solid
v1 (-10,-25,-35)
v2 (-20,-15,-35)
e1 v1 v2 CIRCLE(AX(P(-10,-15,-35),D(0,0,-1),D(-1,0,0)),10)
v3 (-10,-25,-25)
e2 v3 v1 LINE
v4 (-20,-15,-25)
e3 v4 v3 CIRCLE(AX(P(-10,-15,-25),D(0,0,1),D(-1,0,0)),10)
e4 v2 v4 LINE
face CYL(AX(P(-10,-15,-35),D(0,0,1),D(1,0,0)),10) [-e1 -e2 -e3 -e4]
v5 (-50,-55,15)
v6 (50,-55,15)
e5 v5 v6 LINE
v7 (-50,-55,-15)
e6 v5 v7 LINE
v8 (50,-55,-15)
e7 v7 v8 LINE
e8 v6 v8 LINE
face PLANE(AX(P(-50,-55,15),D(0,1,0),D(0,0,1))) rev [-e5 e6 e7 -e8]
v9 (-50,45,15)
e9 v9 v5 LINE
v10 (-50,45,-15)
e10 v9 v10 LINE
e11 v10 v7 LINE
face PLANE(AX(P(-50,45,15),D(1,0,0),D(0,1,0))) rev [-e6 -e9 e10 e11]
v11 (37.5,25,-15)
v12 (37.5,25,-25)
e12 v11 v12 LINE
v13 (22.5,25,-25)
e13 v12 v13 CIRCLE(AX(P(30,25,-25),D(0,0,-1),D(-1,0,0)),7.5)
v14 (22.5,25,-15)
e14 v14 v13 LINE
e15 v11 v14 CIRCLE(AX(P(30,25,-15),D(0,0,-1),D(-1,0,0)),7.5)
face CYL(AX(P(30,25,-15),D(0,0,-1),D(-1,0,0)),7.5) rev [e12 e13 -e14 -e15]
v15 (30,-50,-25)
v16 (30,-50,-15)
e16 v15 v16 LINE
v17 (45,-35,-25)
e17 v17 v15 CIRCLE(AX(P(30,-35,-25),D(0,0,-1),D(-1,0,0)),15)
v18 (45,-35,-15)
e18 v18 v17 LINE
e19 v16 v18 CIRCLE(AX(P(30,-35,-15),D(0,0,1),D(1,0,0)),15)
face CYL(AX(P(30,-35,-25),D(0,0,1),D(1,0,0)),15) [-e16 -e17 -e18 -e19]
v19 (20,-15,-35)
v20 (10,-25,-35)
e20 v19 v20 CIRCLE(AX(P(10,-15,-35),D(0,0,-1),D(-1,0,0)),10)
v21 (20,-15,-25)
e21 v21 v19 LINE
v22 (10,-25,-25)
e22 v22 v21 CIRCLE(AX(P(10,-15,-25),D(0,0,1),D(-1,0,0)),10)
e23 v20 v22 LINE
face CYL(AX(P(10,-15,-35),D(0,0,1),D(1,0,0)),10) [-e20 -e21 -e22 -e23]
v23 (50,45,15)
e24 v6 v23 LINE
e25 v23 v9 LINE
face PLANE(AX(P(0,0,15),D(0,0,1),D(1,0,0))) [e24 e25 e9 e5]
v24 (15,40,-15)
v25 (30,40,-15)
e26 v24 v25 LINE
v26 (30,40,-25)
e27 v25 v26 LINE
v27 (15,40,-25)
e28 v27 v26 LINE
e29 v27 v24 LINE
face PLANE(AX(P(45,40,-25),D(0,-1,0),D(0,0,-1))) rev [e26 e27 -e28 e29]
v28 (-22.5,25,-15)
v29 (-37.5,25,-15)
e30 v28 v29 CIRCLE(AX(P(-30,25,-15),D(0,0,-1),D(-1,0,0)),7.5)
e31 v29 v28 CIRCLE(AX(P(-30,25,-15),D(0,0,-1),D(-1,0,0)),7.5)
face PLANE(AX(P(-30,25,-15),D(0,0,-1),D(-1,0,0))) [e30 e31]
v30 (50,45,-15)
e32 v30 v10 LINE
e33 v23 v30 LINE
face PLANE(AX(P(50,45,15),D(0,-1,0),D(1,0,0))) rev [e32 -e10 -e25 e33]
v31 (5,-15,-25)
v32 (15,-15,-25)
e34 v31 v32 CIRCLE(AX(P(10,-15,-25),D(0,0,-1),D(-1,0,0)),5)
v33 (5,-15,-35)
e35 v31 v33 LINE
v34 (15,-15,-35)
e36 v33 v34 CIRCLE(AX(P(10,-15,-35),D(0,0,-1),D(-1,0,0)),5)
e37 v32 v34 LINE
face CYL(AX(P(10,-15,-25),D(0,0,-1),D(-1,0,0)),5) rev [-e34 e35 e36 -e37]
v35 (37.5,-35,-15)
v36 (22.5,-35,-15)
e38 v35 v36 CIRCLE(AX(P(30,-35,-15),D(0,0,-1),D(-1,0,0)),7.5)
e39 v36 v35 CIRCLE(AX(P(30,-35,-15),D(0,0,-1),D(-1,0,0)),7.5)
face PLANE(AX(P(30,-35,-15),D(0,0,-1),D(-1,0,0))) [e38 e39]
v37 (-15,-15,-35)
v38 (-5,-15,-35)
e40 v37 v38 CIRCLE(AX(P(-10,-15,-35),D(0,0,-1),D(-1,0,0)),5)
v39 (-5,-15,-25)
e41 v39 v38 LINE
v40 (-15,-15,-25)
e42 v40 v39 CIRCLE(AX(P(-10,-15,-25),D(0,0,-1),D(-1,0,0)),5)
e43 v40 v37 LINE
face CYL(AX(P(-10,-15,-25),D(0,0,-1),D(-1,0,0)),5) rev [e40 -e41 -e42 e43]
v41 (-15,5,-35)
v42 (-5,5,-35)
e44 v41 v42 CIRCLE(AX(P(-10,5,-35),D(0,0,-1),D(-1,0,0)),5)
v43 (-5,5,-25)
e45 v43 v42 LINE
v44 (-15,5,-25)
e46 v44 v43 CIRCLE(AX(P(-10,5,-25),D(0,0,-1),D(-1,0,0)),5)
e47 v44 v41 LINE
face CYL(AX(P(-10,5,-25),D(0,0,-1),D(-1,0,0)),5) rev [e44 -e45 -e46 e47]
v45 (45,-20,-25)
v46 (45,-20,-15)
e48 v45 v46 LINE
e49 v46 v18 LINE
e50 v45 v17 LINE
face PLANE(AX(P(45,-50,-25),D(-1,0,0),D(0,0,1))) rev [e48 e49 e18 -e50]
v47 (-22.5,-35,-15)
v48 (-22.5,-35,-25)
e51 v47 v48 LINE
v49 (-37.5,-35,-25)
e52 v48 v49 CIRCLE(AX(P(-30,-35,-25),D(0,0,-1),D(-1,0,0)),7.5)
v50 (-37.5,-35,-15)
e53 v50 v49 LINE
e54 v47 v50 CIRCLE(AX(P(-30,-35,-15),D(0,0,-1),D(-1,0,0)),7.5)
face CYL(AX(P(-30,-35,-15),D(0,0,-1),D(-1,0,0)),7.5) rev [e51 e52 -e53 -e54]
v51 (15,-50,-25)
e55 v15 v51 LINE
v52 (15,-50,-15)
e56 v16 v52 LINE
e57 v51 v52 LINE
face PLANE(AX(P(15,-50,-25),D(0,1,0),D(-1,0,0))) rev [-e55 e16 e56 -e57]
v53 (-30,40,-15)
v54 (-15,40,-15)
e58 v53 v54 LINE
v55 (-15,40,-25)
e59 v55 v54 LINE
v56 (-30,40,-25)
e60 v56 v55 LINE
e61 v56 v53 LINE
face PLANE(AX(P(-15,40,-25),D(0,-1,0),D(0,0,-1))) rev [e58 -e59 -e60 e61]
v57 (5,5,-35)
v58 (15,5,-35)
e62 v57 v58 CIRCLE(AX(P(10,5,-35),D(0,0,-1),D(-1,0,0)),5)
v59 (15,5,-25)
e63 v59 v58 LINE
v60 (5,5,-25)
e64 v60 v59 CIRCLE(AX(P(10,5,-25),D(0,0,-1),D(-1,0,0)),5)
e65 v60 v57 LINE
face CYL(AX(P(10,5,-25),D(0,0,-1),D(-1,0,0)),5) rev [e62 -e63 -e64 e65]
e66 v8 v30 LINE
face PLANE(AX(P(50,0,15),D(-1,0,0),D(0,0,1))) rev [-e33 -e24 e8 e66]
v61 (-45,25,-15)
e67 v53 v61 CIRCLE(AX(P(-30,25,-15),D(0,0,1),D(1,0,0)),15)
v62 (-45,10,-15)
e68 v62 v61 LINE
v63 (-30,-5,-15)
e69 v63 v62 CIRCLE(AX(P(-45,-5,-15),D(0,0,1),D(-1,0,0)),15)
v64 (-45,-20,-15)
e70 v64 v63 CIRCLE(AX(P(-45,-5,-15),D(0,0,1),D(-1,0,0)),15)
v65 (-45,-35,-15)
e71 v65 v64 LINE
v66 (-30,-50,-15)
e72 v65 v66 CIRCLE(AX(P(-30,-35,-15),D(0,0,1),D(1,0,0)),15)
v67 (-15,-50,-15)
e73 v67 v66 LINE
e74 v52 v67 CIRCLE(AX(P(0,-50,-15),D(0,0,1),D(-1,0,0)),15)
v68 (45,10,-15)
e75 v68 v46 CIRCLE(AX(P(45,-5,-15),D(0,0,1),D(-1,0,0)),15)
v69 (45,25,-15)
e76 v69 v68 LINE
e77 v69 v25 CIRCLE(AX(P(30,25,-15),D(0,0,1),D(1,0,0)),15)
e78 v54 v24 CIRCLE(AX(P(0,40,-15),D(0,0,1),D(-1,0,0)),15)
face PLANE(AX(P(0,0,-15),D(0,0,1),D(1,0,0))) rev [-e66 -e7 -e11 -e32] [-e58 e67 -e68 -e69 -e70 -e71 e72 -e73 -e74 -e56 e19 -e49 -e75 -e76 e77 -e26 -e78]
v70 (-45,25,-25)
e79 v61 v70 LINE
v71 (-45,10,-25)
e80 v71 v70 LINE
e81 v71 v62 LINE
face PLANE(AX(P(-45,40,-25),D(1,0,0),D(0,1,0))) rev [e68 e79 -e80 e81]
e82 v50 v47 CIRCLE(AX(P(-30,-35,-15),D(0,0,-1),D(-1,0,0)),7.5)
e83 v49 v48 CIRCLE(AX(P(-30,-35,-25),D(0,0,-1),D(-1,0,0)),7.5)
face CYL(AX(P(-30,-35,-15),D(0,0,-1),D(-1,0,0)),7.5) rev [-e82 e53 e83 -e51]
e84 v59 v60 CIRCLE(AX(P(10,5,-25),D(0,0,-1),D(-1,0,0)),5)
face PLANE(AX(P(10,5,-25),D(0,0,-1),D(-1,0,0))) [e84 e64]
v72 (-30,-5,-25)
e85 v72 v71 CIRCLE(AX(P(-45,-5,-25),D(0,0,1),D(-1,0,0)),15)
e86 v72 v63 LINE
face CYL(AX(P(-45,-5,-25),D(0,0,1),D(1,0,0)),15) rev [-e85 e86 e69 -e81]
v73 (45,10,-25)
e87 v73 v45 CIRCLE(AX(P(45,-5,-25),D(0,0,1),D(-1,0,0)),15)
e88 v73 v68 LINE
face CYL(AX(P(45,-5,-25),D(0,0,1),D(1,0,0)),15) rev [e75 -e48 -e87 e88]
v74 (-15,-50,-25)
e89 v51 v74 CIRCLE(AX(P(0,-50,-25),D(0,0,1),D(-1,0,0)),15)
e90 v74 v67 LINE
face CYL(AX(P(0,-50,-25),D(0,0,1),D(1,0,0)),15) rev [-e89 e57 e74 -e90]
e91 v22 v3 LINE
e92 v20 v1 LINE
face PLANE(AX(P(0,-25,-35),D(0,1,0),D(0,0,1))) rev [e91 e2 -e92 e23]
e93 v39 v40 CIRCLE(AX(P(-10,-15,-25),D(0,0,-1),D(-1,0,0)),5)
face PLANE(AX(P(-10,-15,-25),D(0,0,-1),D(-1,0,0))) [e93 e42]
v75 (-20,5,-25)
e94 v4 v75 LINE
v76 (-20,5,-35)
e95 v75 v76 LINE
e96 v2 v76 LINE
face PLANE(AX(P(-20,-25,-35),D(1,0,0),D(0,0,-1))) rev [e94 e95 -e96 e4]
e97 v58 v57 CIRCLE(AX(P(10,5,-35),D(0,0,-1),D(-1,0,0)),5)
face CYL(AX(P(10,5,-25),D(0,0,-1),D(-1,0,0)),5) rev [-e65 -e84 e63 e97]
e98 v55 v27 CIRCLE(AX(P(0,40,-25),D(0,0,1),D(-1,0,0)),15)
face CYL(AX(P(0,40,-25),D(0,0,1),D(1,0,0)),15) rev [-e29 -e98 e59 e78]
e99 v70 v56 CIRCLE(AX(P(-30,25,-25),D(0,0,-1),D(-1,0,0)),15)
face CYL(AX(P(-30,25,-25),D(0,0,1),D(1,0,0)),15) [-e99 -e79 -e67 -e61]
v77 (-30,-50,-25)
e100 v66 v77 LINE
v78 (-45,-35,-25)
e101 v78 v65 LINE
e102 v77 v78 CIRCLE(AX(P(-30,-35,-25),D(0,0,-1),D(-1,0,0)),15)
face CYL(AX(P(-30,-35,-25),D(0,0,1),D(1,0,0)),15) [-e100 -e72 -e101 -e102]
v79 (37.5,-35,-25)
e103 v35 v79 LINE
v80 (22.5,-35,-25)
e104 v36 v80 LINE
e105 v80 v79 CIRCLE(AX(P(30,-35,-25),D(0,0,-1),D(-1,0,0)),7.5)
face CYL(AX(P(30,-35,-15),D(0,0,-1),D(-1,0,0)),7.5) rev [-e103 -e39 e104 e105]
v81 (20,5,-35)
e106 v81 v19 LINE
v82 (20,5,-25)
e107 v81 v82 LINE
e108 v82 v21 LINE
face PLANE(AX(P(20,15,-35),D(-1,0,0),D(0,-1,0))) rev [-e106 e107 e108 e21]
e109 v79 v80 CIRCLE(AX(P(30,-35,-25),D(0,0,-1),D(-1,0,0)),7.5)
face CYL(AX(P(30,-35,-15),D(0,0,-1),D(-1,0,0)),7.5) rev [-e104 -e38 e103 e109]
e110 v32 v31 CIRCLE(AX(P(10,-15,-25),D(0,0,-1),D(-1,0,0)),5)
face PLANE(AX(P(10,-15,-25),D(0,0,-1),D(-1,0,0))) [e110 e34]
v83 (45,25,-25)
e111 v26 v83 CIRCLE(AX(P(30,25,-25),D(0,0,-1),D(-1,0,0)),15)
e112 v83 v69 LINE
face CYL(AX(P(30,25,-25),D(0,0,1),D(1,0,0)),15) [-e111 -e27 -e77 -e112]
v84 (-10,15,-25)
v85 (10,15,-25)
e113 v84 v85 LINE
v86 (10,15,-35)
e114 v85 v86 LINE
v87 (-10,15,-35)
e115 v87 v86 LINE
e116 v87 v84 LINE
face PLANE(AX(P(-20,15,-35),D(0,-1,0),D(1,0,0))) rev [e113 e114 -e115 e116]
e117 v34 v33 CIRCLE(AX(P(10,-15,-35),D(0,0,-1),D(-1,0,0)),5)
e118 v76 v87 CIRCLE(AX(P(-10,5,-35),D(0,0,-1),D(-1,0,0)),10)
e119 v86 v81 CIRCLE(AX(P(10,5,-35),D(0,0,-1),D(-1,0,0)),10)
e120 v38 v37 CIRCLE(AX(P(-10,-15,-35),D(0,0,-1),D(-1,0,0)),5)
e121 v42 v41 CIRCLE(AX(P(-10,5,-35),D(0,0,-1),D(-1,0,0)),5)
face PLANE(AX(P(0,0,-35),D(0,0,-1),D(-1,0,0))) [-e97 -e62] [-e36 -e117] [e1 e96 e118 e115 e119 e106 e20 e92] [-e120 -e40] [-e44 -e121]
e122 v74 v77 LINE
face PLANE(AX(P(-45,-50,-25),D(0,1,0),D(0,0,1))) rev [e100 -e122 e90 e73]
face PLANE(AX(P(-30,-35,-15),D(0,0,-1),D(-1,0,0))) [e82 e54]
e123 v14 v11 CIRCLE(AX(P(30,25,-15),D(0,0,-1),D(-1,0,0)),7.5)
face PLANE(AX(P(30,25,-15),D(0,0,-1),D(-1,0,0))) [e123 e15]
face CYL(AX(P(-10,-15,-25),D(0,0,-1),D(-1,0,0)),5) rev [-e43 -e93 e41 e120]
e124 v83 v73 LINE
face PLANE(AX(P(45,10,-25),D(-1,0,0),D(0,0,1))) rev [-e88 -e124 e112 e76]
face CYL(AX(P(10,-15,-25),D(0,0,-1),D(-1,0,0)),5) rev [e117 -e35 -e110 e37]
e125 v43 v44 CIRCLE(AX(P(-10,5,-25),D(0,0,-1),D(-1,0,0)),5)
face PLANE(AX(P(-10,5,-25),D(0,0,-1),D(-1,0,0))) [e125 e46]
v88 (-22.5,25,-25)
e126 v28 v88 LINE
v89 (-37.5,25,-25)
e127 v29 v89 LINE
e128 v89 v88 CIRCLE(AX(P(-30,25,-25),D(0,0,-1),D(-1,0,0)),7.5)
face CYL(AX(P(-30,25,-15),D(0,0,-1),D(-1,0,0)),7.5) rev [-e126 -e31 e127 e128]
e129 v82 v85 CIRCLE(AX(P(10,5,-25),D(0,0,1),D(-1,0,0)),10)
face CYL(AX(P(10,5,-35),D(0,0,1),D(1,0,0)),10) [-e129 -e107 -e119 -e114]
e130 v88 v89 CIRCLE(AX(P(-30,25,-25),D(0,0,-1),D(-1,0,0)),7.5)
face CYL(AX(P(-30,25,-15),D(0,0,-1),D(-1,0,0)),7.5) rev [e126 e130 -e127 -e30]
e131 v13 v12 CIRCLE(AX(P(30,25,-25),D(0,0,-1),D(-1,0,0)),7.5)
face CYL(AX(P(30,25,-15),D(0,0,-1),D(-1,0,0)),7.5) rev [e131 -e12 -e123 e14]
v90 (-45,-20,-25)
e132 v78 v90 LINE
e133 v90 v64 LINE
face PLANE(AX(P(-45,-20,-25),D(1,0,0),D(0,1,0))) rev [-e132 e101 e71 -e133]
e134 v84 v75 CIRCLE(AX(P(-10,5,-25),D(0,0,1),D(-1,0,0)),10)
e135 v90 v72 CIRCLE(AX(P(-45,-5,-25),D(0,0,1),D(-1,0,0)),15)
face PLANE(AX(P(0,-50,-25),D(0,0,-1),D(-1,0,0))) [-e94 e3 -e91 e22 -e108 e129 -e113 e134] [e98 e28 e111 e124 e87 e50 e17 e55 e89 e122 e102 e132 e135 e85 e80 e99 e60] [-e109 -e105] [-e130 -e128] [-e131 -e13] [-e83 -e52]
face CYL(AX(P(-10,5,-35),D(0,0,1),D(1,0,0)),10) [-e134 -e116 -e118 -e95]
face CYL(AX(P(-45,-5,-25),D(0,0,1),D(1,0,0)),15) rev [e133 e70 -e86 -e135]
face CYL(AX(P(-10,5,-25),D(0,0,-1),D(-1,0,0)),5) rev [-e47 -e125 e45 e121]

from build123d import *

# Parameters (mm, degrees)
BASE_BLOCK_100X100X30_DEPTH        = 15
LOCATING_PADS_10MM_DEPTH           = 10
LOCATING_PAD_FILLET_R15_1_R        = 15
LOCATING_PAD_FILLET_R15_2_R        = 15
LOCATING_PAD_FILLET_R15_3_R        = 15
LOCATING_PAD_FILLET_R15_4_R        = 15
RAISED_PAD_10MM_DEPTH              = 10
RAISED_PAD_FILLET_R10_1_R          = 10
RAISED_PAD_FILLET_R10_2_R          = 10
RAISED_PAD_FILLET_R10_3_R          = 10
RAISED_PAD_FILLET_R10_4_R          = 10
RAISED_PAD_POCKET_SKETCH_R         = 5
RAISED_PAD_POCKET_10X10X10_DEPTH   = 10
LOCATING_PAD_POCKET_SKETCH_R       = 7.5
LOCATING_PAD_POCKET_15X15X10_DEPTH = 10


with BuildPart() as part:
    # Base Block Sketch → Base Block 100x100x30 (new, symmetric)
    with BuildSketch(Plane.XY):
        Polygon((50, 45), (-50, 45), (-50, -55), (50, -55), (50, 0), align=None)
    extrude(amount=BASE_BLOCK_100X100X30_DEPTH, both=True)

    # Locating Pads Sketch → Locating Pads 10mm (add)
    with BuildSketch(Plane(origin=(0, 0, -15), x_dir=(-1, 0, 0), z_dir=(0, 0, -1))):
        with BuildLine():
            Line((15, 40), (45, 40))
            Line((45, 40), (45, 10))
            ThreePointArc((45, 10), (30, -5), (45, -20))
            Line((45, -20), (45, -50))
            Line((45, -50), (15, -50))
            ThreePointArc((15, -50), (0, -35), (-15, -50))
            Line((-15, -50), (-45, -50))
            Line((-45, -50), (-45, -20))
            ThreePointArc((-45, -20), (-30, -5), (-45, 10))
            Line((-45, 10), (-45, 40))
            Line((-45, 40), (-15, 40))
            ThreePointArc((-15, 40), (0, 25), (15, 40))
        make_face()
    extrude(amount=LOCATING_PADS_10MM_DEPTH)

    # Locating Pad Fillet R15 1
    locating_pad_fillet_r15_1_edges = [part.edges().sort_by_distance(p)[0] for p in [
        (-45, -50, -20),
    ]]
    fillet(locating_pad_fillet_r15_1_edges, radius=LOCATING_PAD_FILLET_R15_1_R)

    # Locating Pad Fillet R15 2
    locating_pad_fillet_r15_2_edges = [part.edges().sort_by_distance(p)[0] for p in [
        (45, -50, -20),
    ]]
    fillet(locating_pad_fillet_r15_2_edges, radius=LOCATING_PAD_FILLET_R15_2_R)

    # Locating Pad Fillet R15 3
    locating_pad_fillet_r15_3_edges = [part.edges().sort_by_distance(p)[0] for p in [
        (45, 40, -20),
    ]]
    fillet(locating_pad_fillet_r15_3_edges, radius=LOCATING_PAD_FILLET_R15_3_R)

    # Locating Pad Fillet R15 4
    locating_pad_fillet_r15_4_edges = [part.edges().sort_by_distance(p)[0] for p in [
        (-45, 40, -20),
    ]]
    fillet(locating_pad_fillet_r15_4_edges, radius=LOCATING_PAD_FILLET_R15_4_R)

    # Raised Pad Sketch → Raised Pad 10mm (add)
    with BuildSketch(Plane(origin=(0, 0, -25), x_dir=(-1, 0, 0), z_dir=(0, 0, -1))):
        Polygon((0, -25), (20, -25), (20, 15), (-20, 15), (-20, -25), align=None)
    extrude(amount=RAISED_PAD_10MM_DEPTH)

    # Raised Pad Fillet R10 1
    raised_pad_fillet_r10_1_edges = [part.edges().sort_by_distance(p)[0] for p in [
        (20, -25, -30),
    ]]
    fillet(raised_pad_fillet_r10_1_edges, radius=RAISED_PAD_FILLET_R10_1_R)

    # Raised Pad Fillet R10 2
    raised_pad_fillet_r10_2_edges = [part.edges().sort_by_distance(p)[0] for p in [
        (20, 15, -30),
    ]]
    fillet(raised_pad_fillet_r10_2_edges, radius=RAISED_PAD_FILLET_R10_2_R)

    # Raised Pad Fillet R10 3
    raised_pad_fillet_r10_3_edges = [part.edges().sort_by_distance(p)[0] for p in [
        (-20, 15, -30),
    ]]
    fillet(raised_pad_fillet_r10_3_edges, radius=RAISED_PAD_FILLET_R10_3_R)

    # Raised Pad Fillet R10 4
    raised_pad_fillet_r10_4_edges = [part.edges().sort_by_distance(p)[0] for p in [
        (-20, -25, -30),
    ]]
    fillet(raised_pad_fillet_r10_4_edges, radius=RAISED_PAD_FILLET_R10_4_R)

    # Raised Pad Pocket Sketch → Raised Pad Pocket 10x10x10 (cut)
    with BuildSketch(Plane(origin=(0, 0, -35), x_dir=(-1, 0, 0), z_dir=(0, 0, -1))):
        with Locations((10, 5)):
            Circle(RAISED_PAD_POCKET_SKETCH_R)
        with Locations((10, -15)):
            Circle(RAISED_PAD_POCKET_SKETCH_R)
        with Locations((-10, -15)):
            Circle(RAISED_PAD_POCKET_SKETCH_R)
        with Locations((-10, 5)):
            Circle(RAISED_PAD_POCKET_SKETCH_R)
    extrude(amount=-RAISED_PAD_POCKET_10X10X10_DEPTH, mode=Mode.SUBTRACT)

    # Locating Pad Pocket Sketch → Locating Pad Pocket 15x15x10 (cut)
    with BuildSketch(Plane(origin=(0, 0, -25), x_dir=(-1, 0, 0), z_dir=(0, 0, -1))):
        with Locations((30, 25)):
            Circle(LOCATING_PAD_POCKET_SKETCH_R)
        with Locations((30, -35)):
            Circle(LOCATING_PAD_POCKET_SKETCH_R)
        with Locations((-30, -35)):
            Circle(LOCATING_PAD_POCKET_SKETCH_R)
        with Locations((-30, 25)):
            Circle(LOCATING_PAD_POCKET_SKETCH_R)
    extrude(amount=-LOCATING_PAD_POCKET_15X15X10_DEPTH, mode=Mode.SUBTRACT)


solid = part.part
